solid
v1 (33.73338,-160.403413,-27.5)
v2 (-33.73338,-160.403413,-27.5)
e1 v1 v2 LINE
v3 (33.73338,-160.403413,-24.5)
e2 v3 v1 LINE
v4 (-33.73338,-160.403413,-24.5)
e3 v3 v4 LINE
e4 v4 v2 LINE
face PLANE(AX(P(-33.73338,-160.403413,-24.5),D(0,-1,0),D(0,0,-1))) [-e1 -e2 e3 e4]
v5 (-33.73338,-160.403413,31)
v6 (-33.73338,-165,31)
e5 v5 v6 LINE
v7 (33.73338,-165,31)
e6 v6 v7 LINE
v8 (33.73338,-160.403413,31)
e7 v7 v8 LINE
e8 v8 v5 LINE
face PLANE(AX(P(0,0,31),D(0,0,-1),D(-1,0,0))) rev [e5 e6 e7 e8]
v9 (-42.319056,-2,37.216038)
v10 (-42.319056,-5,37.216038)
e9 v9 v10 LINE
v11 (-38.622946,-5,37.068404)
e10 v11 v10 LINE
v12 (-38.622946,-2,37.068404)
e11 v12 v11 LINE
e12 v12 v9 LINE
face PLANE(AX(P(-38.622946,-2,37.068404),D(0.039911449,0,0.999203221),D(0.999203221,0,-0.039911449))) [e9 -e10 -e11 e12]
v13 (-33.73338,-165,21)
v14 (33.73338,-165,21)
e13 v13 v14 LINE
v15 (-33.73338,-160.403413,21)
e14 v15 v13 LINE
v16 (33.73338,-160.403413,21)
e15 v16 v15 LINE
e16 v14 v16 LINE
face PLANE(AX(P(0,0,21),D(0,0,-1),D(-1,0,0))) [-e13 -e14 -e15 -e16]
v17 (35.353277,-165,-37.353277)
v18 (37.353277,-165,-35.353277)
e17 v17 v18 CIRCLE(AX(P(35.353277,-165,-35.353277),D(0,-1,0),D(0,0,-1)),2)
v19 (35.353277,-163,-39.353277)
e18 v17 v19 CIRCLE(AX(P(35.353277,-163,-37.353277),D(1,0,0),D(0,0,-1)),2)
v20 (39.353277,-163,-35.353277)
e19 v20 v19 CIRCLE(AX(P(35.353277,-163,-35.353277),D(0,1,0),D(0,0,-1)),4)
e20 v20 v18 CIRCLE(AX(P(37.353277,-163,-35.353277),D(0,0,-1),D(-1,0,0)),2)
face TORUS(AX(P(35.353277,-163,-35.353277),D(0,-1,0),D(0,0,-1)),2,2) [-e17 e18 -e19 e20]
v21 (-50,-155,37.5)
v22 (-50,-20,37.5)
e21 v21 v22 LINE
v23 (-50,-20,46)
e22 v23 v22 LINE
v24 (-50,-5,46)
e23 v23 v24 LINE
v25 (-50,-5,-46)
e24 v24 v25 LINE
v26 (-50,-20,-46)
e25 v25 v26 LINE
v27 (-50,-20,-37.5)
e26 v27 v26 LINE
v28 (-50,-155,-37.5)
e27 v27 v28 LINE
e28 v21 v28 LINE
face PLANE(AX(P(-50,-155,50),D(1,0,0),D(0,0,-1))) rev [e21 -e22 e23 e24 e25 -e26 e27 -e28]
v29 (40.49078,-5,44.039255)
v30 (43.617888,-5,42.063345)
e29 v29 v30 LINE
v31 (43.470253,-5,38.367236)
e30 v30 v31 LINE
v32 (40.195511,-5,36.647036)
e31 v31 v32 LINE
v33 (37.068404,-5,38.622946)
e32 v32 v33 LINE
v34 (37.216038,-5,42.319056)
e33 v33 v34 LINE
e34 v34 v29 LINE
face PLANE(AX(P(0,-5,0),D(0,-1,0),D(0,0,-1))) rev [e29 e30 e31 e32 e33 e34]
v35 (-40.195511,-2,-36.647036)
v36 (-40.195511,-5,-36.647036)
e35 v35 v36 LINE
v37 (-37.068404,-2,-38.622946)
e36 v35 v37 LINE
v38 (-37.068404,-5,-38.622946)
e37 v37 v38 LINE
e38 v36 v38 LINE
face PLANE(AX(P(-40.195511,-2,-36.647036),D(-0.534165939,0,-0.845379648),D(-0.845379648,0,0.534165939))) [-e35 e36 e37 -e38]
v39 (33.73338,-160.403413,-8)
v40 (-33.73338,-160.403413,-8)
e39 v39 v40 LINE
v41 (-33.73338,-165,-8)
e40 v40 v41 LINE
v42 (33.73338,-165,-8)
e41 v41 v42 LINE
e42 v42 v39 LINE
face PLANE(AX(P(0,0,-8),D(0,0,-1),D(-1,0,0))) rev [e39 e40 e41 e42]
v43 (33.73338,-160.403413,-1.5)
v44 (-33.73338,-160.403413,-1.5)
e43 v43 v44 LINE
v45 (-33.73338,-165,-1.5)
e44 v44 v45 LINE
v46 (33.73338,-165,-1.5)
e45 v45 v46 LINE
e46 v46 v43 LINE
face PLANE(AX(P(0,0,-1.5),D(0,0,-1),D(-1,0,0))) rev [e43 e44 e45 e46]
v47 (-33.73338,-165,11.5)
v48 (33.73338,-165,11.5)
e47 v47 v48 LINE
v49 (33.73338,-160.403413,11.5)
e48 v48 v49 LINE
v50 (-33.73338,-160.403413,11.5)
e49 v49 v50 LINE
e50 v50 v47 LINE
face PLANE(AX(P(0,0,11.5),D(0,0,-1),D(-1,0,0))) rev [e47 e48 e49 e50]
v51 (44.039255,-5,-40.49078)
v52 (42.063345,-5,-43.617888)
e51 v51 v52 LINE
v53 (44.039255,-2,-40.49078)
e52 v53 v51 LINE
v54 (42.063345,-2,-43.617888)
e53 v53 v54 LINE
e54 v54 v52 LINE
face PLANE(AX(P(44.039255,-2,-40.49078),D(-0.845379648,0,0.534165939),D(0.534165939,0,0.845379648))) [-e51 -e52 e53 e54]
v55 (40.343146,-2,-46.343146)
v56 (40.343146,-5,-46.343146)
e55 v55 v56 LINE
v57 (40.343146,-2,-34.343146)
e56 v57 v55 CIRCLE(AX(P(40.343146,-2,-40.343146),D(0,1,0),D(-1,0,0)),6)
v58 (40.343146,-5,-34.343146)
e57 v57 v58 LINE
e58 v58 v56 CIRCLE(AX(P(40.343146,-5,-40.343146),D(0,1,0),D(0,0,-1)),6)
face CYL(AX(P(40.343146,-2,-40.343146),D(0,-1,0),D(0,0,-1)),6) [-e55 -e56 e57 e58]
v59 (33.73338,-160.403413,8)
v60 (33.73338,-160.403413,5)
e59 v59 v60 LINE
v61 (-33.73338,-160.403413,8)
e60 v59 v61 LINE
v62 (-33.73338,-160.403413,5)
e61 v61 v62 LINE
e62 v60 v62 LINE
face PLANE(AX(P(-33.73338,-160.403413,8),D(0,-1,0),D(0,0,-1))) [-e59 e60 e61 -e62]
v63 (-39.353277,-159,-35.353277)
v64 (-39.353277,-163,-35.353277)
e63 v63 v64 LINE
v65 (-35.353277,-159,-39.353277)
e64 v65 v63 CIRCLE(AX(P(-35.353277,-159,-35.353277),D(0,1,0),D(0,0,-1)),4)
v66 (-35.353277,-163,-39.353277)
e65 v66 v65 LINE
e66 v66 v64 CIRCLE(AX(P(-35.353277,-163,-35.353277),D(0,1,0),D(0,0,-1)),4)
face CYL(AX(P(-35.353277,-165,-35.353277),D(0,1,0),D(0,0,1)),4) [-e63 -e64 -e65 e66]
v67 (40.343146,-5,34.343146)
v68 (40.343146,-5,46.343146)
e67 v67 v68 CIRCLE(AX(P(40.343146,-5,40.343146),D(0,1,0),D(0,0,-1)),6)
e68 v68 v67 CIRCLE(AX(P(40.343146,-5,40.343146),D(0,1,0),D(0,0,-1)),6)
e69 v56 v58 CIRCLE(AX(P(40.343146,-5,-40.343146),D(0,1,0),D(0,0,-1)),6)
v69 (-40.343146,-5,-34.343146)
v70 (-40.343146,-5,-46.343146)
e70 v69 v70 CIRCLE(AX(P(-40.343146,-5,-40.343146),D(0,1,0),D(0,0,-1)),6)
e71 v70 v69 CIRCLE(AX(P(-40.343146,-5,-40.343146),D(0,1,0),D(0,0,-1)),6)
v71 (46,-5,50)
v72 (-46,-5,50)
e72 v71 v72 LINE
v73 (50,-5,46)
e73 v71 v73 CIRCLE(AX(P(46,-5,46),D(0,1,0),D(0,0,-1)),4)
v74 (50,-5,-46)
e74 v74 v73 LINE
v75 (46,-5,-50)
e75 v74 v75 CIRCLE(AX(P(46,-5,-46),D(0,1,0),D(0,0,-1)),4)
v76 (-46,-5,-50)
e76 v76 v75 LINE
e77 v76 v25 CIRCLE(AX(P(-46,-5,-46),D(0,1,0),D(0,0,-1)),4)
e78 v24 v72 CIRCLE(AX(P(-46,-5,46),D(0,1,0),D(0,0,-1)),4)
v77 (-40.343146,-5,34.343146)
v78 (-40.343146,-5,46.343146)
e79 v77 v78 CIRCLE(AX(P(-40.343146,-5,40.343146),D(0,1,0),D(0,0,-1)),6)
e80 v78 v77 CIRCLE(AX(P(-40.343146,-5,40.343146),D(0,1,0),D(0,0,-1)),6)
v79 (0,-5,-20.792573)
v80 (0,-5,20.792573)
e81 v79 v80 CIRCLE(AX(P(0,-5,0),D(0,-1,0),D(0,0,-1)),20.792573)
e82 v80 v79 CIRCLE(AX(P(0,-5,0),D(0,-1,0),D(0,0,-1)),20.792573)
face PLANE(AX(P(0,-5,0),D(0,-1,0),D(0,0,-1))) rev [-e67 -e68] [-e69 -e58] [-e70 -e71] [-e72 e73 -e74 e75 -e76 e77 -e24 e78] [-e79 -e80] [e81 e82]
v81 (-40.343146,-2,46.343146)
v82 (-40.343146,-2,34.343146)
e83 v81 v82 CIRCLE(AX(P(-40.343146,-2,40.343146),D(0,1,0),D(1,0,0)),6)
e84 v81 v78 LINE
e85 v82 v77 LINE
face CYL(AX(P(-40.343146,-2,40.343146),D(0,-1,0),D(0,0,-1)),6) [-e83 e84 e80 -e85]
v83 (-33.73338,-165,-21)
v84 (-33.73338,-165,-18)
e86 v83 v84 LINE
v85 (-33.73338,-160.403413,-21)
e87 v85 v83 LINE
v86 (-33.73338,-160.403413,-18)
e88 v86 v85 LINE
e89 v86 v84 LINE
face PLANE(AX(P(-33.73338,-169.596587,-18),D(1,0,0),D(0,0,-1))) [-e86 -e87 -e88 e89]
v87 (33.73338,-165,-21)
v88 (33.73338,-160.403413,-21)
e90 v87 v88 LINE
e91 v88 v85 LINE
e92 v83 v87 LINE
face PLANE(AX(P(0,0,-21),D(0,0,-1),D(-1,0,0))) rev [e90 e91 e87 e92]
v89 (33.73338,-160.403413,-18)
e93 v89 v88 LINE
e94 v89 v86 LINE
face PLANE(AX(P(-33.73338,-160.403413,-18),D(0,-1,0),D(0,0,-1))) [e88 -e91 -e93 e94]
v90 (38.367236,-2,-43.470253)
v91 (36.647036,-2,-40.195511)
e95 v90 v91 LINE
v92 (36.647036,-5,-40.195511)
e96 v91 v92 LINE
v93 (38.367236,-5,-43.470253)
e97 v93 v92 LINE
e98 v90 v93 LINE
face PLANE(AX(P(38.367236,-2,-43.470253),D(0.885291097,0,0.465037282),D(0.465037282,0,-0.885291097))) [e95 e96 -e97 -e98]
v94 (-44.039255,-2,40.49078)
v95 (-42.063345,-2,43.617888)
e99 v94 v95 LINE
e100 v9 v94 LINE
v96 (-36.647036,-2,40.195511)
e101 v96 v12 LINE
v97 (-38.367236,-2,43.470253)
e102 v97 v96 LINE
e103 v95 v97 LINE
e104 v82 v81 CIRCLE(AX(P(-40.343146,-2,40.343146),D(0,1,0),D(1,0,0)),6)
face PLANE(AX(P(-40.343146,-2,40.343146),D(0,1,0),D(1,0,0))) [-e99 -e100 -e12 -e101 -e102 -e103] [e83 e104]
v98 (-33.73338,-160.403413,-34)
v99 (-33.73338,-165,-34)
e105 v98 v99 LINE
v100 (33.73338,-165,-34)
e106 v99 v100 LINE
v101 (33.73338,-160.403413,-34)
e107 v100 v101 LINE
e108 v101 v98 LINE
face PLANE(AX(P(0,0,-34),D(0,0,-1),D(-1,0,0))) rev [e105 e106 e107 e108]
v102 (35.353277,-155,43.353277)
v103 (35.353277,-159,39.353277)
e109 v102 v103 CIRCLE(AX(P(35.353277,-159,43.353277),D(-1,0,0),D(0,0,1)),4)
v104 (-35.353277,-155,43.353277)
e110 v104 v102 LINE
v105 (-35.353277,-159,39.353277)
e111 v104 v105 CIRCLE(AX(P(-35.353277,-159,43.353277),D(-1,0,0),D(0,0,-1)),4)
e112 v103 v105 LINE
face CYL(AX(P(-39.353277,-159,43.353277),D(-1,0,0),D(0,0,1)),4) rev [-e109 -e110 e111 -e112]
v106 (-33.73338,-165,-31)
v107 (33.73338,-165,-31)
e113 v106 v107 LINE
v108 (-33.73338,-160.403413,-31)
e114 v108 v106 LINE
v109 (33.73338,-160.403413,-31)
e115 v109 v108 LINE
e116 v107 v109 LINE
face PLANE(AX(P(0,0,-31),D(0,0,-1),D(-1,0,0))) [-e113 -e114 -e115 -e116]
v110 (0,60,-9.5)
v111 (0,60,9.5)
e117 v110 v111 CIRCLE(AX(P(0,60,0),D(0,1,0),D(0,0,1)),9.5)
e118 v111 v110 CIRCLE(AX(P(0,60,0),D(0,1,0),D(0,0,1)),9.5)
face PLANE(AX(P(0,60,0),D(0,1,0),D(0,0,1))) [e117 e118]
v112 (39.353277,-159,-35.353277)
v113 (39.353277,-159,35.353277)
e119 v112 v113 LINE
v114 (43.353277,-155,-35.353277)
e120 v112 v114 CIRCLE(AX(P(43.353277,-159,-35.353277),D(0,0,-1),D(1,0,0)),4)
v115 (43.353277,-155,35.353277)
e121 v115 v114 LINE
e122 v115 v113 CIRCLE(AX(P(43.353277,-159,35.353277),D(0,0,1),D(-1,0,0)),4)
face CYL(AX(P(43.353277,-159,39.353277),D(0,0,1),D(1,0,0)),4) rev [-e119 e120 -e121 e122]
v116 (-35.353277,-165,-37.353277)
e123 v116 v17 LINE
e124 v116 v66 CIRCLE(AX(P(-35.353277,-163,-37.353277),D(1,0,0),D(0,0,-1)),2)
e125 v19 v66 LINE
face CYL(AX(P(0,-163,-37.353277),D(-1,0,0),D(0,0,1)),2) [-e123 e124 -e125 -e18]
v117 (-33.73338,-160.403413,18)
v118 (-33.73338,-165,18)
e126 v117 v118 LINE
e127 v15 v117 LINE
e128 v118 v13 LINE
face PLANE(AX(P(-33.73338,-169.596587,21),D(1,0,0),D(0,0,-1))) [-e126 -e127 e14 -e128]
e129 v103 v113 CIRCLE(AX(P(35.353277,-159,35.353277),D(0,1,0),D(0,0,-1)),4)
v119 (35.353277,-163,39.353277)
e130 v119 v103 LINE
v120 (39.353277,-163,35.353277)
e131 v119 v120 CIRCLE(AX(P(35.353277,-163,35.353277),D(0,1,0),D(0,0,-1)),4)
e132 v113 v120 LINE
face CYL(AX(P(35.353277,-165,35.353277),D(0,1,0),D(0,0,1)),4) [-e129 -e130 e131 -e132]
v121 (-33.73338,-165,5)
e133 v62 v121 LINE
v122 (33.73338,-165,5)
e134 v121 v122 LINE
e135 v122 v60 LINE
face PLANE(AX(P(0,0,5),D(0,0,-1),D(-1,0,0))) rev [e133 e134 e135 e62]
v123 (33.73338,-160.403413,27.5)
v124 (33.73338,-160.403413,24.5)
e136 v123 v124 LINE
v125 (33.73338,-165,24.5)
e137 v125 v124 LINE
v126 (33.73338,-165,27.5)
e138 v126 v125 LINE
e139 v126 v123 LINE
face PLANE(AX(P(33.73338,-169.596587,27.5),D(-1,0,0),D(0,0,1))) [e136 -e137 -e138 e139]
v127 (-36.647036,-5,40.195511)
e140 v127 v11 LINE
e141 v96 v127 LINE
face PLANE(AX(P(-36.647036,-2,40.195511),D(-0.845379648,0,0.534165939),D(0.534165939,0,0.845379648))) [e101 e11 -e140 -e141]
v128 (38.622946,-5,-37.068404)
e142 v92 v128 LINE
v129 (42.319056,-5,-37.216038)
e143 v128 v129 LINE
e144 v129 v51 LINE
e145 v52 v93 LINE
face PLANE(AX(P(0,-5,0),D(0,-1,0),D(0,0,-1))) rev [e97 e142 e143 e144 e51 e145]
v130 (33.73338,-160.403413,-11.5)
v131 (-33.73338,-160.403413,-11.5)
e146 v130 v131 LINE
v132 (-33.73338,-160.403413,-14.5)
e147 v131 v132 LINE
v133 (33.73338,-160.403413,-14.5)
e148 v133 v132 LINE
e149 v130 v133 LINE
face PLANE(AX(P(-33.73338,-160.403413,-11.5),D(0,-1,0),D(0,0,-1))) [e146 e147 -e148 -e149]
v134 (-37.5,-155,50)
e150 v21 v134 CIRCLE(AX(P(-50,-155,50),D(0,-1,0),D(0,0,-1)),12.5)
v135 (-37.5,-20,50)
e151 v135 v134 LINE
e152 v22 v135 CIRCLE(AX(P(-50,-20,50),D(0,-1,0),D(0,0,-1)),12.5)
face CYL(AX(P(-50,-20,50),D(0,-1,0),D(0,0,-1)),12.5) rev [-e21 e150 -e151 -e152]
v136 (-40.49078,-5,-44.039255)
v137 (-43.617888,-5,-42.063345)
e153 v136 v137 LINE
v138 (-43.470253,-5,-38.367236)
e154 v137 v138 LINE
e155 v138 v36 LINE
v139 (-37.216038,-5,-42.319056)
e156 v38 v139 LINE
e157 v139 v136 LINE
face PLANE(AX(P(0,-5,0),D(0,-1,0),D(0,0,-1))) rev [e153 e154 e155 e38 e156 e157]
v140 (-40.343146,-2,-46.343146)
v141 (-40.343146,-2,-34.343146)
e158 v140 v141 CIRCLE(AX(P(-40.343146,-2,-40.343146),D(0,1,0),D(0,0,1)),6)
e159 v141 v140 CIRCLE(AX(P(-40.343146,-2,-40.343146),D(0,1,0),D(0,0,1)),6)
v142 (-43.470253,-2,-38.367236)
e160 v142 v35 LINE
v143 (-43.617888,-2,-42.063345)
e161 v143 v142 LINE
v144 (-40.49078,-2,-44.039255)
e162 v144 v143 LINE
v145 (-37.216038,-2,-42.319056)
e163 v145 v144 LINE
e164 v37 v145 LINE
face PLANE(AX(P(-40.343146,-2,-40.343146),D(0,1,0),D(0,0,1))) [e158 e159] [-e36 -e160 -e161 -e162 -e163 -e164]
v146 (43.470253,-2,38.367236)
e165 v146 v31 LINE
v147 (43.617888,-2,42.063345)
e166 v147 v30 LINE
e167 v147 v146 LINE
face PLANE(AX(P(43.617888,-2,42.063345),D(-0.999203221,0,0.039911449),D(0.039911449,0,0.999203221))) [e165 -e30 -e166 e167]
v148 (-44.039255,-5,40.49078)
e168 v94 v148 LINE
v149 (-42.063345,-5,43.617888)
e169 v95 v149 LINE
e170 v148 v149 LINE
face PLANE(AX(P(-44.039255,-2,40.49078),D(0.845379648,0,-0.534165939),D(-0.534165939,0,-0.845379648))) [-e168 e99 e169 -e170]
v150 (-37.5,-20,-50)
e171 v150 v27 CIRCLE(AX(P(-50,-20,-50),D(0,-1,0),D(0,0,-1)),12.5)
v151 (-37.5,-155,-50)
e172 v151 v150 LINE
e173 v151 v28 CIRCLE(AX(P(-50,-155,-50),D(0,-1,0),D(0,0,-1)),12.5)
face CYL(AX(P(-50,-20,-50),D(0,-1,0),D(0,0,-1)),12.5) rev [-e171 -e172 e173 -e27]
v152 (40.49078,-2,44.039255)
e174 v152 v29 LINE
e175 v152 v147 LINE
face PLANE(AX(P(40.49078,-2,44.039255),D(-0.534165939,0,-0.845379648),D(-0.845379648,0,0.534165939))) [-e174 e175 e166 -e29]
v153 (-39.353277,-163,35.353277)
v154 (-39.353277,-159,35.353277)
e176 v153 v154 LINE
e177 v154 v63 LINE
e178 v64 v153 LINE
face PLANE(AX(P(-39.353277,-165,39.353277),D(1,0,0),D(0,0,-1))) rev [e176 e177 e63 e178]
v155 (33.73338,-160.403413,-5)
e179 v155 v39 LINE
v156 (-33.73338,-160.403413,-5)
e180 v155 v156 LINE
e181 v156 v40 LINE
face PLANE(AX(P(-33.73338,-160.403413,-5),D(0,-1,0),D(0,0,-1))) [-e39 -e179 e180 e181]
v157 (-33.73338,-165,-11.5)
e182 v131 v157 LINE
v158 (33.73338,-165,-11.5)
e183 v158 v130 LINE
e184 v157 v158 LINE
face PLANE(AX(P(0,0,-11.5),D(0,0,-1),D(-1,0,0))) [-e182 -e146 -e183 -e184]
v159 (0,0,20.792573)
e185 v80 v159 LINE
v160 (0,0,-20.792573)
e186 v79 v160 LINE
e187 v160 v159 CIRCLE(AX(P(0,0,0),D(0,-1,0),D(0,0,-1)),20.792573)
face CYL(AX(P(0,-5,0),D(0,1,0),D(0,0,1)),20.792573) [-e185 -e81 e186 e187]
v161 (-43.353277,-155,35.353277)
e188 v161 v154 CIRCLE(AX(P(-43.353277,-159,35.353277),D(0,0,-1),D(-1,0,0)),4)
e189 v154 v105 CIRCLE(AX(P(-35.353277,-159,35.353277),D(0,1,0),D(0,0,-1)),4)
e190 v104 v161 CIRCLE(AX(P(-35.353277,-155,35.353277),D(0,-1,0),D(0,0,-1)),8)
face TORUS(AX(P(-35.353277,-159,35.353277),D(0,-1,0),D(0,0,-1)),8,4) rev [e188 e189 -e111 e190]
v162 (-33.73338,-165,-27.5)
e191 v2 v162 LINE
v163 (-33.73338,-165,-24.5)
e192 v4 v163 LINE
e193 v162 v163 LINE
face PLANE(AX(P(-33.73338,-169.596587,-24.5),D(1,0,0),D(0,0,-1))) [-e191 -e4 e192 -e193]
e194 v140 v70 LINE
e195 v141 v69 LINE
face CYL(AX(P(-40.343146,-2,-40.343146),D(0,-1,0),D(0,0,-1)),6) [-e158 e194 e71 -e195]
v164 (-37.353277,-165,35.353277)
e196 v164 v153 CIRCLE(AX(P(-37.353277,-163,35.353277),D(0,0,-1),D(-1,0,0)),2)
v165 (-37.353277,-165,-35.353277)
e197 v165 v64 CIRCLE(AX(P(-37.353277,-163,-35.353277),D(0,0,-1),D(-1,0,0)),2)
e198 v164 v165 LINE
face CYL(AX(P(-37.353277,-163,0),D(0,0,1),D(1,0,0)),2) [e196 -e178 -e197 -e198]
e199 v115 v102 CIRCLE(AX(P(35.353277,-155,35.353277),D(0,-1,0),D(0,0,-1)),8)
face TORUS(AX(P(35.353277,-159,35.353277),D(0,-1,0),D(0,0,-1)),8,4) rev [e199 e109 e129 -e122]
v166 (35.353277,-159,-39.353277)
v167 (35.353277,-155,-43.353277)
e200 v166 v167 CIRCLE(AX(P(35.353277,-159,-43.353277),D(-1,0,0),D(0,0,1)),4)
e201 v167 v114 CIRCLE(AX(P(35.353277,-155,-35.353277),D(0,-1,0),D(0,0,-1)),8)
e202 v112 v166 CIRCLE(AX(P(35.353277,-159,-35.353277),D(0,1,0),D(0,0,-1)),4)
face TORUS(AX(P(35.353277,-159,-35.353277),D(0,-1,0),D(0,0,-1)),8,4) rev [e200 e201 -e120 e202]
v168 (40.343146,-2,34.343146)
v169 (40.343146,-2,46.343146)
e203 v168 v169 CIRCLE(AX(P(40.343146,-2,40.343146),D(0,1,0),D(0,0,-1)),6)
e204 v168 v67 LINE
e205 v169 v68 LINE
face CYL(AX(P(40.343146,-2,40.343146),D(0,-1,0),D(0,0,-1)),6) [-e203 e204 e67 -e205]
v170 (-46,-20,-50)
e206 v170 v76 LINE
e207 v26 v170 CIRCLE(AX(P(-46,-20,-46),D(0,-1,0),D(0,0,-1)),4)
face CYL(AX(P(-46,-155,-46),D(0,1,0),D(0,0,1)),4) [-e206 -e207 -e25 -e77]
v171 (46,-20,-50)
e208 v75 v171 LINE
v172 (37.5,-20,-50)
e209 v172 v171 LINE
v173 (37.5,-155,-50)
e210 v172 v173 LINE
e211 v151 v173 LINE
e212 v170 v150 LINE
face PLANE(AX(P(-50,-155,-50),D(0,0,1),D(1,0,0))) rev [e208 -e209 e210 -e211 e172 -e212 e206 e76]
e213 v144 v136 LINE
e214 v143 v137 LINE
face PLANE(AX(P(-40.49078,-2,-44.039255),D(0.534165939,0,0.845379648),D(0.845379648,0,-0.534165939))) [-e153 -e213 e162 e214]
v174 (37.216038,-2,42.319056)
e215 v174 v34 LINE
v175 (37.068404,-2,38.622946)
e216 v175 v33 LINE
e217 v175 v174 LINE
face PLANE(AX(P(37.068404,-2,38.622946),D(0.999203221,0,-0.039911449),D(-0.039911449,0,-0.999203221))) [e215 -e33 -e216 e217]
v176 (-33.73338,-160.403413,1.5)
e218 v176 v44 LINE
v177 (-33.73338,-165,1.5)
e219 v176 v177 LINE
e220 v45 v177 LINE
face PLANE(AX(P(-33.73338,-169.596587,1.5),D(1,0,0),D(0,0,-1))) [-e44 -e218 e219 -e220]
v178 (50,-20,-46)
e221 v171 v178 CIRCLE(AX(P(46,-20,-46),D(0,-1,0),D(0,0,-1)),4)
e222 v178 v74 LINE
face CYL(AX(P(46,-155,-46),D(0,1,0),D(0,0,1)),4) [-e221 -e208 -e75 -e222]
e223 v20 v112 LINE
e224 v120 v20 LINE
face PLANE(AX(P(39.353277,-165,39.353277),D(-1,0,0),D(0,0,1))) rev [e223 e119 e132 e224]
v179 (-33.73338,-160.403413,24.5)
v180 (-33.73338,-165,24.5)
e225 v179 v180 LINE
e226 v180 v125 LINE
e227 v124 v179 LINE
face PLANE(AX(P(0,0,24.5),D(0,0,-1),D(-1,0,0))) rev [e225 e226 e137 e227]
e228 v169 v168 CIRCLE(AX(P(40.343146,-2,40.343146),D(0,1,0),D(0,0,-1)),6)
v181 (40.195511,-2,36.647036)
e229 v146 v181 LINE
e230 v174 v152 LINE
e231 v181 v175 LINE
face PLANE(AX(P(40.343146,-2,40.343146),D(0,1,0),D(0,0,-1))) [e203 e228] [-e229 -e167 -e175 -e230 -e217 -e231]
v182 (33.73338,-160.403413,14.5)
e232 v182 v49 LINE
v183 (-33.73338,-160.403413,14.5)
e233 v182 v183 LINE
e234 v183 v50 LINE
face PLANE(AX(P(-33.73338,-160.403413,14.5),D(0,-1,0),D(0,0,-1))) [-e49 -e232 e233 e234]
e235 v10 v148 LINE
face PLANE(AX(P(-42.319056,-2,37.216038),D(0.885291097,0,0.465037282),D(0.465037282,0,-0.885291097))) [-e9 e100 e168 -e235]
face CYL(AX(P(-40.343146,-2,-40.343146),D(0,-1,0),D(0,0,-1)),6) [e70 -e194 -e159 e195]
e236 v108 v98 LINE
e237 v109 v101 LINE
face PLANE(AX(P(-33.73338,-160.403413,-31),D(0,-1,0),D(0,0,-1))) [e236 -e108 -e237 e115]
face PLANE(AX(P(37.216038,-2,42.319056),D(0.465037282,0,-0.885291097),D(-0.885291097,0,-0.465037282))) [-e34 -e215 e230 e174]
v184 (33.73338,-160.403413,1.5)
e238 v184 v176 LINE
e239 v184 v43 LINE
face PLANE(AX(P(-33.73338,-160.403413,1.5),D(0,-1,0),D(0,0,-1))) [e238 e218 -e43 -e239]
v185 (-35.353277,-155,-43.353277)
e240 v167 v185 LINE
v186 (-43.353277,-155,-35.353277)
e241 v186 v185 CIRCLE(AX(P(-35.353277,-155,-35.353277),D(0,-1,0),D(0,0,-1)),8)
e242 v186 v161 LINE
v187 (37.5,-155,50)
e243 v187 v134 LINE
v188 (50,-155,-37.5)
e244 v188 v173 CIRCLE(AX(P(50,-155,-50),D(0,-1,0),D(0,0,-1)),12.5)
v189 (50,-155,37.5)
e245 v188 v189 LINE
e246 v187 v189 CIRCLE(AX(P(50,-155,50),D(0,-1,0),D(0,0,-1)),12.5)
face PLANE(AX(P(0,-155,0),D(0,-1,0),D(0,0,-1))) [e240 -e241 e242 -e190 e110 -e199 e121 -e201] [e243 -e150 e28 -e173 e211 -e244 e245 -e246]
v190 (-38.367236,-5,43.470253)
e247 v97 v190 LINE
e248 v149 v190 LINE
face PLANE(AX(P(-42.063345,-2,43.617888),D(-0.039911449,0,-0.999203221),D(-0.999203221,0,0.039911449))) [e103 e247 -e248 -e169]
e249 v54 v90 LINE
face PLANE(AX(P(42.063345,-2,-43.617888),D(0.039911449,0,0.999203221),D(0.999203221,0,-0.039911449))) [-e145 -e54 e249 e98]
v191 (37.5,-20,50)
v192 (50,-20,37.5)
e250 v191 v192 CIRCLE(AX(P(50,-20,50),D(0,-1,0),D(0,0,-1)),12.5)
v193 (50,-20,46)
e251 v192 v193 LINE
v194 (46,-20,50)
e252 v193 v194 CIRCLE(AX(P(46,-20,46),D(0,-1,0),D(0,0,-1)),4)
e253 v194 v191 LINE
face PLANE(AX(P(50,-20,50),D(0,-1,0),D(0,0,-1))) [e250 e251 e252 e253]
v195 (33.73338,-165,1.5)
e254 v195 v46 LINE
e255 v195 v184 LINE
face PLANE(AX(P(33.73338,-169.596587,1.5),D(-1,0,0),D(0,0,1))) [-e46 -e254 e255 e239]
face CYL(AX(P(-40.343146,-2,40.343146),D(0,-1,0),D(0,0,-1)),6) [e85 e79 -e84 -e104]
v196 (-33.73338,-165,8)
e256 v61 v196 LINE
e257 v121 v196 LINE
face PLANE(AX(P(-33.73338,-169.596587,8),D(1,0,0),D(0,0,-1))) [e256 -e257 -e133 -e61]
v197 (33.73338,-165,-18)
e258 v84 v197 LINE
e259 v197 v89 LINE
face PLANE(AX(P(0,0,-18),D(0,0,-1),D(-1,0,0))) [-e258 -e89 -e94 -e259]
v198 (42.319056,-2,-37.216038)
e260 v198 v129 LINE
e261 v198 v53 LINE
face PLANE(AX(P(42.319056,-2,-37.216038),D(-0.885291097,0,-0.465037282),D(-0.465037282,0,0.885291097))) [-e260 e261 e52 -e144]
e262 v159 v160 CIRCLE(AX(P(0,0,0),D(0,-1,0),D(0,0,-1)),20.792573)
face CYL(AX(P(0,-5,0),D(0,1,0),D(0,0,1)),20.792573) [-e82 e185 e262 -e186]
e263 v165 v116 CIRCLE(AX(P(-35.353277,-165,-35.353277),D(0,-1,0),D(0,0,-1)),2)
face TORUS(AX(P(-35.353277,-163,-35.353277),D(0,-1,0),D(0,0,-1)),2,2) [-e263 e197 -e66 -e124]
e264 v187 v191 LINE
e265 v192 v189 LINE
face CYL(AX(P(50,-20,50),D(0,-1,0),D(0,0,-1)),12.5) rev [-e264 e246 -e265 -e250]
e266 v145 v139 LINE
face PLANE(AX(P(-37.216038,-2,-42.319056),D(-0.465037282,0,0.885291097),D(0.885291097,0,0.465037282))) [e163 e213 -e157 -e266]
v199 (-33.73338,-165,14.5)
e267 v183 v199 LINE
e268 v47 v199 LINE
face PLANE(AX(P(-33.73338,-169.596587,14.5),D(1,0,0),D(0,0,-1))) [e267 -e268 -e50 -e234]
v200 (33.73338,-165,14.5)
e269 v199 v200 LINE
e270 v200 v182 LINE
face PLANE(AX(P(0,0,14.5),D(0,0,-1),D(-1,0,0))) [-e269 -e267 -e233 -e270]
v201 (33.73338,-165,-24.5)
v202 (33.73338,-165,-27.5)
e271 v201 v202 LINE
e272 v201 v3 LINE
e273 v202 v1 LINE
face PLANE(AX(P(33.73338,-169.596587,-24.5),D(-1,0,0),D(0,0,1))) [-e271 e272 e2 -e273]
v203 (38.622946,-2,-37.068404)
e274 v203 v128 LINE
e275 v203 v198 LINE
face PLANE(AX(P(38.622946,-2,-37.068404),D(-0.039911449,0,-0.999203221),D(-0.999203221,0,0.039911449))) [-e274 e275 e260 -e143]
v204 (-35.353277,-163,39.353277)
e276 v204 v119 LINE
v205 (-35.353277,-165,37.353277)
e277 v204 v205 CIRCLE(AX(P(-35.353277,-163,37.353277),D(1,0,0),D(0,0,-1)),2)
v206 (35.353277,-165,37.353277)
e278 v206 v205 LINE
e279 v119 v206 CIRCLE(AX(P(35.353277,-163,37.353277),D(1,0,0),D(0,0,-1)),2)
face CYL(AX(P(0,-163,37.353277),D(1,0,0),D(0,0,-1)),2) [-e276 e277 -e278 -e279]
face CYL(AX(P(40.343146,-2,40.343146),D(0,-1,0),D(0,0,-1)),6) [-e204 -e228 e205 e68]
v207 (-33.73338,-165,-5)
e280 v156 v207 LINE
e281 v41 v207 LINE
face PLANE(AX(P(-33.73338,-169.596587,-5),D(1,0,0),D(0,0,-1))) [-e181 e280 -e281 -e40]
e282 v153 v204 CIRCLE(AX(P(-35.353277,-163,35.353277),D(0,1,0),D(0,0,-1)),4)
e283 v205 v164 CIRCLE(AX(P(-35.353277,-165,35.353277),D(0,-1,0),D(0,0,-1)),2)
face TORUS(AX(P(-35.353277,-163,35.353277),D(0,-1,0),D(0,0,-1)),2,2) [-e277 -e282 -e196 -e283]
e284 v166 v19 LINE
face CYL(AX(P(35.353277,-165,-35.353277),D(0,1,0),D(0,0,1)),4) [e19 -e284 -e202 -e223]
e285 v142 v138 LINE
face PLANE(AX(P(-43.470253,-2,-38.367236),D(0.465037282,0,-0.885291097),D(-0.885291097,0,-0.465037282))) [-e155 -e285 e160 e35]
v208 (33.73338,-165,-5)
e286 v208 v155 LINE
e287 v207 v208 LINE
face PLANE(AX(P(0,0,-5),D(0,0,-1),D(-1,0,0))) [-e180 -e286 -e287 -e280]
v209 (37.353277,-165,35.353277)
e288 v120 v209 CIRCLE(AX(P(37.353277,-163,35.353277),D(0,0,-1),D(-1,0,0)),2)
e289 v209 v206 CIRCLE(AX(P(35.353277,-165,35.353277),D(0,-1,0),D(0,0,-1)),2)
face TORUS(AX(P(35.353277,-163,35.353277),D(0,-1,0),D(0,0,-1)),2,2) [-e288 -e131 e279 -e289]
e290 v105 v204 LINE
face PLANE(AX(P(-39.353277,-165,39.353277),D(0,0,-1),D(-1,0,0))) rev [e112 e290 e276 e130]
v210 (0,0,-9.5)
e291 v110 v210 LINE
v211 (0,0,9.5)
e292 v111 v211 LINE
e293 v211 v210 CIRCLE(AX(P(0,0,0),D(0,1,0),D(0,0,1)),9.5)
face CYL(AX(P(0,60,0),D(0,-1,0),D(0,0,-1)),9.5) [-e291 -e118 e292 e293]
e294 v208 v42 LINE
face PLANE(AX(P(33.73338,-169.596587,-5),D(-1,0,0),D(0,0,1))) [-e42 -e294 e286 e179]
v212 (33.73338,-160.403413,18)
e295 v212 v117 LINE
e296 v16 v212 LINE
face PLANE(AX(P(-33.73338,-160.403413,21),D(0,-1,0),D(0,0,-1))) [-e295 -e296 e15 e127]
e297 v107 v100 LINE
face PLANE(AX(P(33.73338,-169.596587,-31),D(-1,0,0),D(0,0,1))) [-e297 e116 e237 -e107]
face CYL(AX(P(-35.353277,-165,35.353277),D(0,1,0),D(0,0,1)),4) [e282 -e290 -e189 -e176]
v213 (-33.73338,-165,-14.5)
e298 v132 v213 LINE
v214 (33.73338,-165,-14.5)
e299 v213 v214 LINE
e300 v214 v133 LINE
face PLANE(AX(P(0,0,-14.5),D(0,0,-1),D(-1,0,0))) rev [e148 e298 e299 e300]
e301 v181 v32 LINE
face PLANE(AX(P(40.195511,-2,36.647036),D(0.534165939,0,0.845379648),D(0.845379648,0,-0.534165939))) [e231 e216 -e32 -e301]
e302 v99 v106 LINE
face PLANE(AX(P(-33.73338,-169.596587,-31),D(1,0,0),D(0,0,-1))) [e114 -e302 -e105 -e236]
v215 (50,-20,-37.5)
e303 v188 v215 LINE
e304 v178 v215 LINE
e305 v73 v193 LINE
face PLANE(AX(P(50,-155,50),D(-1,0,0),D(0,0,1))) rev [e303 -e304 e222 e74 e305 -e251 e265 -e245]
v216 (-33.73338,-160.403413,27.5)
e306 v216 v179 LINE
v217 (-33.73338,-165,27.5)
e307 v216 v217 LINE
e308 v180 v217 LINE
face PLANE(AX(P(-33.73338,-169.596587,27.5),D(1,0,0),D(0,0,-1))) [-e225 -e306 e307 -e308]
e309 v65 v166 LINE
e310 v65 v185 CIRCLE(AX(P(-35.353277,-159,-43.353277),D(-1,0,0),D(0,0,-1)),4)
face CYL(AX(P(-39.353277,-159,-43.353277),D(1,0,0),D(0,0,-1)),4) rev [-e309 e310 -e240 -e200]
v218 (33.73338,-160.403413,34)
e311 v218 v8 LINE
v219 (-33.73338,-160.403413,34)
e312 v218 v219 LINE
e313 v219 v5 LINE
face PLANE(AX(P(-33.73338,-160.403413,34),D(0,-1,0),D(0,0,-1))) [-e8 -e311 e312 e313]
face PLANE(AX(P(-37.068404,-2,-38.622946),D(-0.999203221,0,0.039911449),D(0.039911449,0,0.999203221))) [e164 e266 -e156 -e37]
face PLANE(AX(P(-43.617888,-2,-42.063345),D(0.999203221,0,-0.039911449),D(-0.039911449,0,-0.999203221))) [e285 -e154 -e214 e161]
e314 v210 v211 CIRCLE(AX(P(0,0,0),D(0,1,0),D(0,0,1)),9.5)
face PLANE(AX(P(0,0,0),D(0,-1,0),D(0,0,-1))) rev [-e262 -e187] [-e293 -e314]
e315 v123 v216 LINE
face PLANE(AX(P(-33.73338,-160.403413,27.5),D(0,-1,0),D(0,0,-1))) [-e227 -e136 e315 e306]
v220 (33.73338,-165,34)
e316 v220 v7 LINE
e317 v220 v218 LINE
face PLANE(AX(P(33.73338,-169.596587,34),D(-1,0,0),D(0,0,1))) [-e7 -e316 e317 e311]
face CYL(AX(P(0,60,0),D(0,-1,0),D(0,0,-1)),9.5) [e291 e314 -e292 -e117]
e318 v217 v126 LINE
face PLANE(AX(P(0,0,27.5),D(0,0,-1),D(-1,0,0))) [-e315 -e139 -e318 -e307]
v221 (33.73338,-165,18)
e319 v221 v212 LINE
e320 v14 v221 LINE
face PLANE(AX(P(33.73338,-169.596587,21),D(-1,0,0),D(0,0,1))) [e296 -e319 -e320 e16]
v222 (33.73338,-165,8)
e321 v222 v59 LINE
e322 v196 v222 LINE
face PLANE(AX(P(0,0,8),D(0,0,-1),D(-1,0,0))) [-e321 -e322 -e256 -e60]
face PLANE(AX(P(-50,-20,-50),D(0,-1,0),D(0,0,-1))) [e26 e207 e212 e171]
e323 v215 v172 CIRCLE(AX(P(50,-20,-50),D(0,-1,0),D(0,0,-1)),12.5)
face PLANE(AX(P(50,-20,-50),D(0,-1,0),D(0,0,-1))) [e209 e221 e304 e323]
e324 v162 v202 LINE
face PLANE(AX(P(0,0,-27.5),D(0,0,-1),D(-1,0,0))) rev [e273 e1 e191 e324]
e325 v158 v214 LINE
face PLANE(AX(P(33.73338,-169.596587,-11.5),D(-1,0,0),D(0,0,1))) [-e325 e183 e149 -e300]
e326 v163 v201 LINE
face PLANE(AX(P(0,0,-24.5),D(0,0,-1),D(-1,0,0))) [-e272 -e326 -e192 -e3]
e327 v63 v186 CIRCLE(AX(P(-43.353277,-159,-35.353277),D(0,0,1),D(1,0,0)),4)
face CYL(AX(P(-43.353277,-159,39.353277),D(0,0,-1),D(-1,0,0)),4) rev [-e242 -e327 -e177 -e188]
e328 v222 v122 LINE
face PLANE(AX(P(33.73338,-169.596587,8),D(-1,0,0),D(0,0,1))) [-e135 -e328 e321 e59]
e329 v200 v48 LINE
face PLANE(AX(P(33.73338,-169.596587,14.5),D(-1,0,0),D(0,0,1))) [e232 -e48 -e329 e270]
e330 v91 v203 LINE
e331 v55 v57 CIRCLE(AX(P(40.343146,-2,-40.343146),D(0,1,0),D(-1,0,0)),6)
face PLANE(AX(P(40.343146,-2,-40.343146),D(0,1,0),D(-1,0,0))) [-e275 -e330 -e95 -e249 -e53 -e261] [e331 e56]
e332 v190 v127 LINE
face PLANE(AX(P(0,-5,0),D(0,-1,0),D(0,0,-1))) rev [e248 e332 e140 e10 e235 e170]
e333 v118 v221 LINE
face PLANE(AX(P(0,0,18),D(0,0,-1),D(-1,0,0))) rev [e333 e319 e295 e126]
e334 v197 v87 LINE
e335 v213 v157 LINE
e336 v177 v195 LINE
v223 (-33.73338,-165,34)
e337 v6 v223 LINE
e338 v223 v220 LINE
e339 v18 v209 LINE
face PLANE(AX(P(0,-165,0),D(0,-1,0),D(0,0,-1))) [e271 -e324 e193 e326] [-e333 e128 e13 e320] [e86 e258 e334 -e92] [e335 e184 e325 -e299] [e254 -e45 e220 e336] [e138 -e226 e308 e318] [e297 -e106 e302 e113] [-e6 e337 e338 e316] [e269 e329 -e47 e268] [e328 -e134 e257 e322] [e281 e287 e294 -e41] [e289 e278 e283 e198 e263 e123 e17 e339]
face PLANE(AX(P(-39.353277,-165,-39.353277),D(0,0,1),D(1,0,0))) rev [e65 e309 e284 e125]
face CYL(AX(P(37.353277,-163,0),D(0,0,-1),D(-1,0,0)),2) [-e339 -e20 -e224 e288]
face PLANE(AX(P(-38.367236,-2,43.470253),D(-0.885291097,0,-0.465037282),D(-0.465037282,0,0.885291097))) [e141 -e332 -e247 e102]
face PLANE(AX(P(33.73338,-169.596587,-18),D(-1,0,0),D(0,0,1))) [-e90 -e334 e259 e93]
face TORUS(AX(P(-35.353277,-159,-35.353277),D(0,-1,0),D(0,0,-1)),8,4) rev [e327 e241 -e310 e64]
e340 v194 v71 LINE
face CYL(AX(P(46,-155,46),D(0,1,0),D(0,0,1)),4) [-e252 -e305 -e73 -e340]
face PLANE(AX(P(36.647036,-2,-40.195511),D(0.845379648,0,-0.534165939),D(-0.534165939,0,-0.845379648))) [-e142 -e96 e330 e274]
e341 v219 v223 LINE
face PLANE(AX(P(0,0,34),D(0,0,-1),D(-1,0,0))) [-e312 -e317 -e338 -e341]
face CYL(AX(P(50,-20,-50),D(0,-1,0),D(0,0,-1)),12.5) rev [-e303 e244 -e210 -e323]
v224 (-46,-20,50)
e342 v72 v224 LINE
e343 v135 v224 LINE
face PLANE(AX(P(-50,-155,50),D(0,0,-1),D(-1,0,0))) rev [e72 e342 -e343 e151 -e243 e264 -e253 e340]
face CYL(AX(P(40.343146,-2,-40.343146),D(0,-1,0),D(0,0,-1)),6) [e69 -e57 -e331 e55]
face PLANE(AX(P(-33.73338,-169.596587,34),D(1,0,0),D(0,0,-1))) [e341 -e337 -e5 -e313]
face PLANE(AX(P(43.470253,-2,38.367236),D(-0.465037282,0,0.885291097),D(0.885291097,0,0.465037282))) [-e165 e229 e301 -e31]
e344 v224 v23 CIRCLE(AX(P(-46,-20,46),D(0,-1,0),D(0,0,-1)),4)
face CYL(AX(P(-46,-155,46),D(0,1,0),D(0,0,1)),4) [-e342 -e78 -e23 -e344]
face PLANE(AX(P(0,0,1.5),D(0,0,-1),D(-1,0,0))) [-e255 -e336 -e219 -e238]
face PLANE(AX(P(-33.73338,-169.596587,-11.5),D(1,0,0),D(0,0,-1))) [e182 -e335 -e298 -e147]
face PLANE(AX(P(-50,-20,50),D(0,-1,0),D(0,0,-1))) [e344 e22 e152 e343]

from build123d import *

# Parameters (mm, degrees)
SKETCH1_R           = 9.5
BOSS_EXTRUDE1_DEPTH = 60
SKETCH2_R           = 20.792572887
BOSS_EXTRUDE2_DEPTH = 5
SKETCH3_W           = 100
SKETCH3_H           = 100
BOSS_EXTRUDE3_DEPTH = 150
SKETCH4_R           = 12.5
CUT_EXTRUDE1_DEPTH  = 135
FILLET1_R           = 4
SKETCH5_W           = 78.706554356
SKETCH5_H           = 78.706554356
BOSS_EXTRUDE4_DEPTH = 10
FILLET2_R           = 4
FILLET3_R           = 2
SKETCH6_W           = 67.46675987
SKETCH6_H           = 9.193174248
CUT_EXTRUDE2_DEPTH  = 1.5
LPATTERN1_COUNT     = 6
LPATTERN1_PITCH     = 6.5
LPATTERN1_COL_COUNT = 6
LPATTERN1_COL_PITCH = 6.5
SKETCH7_R           = 6
BOSS_EXTRUDE5_DEPTH = 3
CIRPATTERN1_COUNT   = 4


with BuildPart() as part:
    # Sketch1 → Boss-Extrude1 (new body)
    with BuildSketch(Plane(origin=(0, 0, 0), x_dir=(1, 0, 0), z_dir=(0, 1, 0))):
        with Locations(Location((0, 0, 0), (0, 0, 270))):
            Circle(SKETCH1_R)
    extrude(amount=BOSS_EXTRUDE1_DEPTH)

    # Sketch2 → Boss-Extrude2 (add)
    with BuildSketch(Plane.XZ):
        with Locations(Location((0, 0, 0), (0, 0, 270))):
            Circle(SKETCH2_R)
    extrude(amount=BOSS_EXTRUDE2_DEPTH)

    # Sketch3 → Boss-Extrude3 (add)
    with BuildSketch(Plane.XZ.offset(5)):
        Rectangle(SKETCH3_W, SKETCH3_H)
    extrude(amount=BOSS_EXTRUDE3_DEPTH)

    # Sketch4 → Cut-Extrude1 (cut)
    with BuildSketch(Plane.XZ.offset(155)):
        with Locations((-50, 50)):
            Circle(SKETCH4_R)
        with Locations((50, 50)):
            Circle(SKETCH4_R)
        with Locations((-50, -50)):
            Circle(SKETCH4_R)
        with Locations((50, -50)):
            Circle(SKETCH4_R)
    extrude(amount=-CUT_EXTRUDE1_DEPTH, mode=Mode.SUBTRACT)

    # Fillet1
    fillet1_edges = [part.edges().sort_by_distance(p)[0] for p in [
        (50, -12.5, -50),
        (-50, -12.5, -50),
        (-50, -12.5, 50),
        (50, -12.5, 50),
    ]]
    fillet(fillet1_edges, radius=FILLET1_R)

    # Sketch5 → Boss-Extrude4 (add)
    with BuildSketch(Plane.XZ.offset(155)):
        Rectangle(SKETCH5_W, SKETCH5_H)
    extrude(amount=BOSS_EXTRUDE4_DEPTH)

    # Fillet2
    fillet2_edges = [part.edges().sort_by_distance(p)[0] for p in [
        (39.353277178, -155, 0),
        (39.353277178, -160, -39.353277178),
        (0, -155, 39.353277178),
        (39.353277178, -160, 39.353277178),
        (-39.353277178, -155, 0),
        (-39.353277178, -160, 39.353277178),
        (0, -155, -39.353277178),
        (-39.353277178, -160, -39.353277178),
    ]]
    fillet(fillet2_edges, radius=FILLET2_R)

    # Fillet3
    fillet3_edges = [part.edges().sort_by_distance(p)[0] for p in [
        (39.353277178, -165, 0),
        (0, -165, 39.353277178),
        (-39.353277178, -165, 0),
        (0, -165, -39.353277178),
        (38.181704302, -165, -38.181704302),
        (-38.181704302, -165, -38.181704302),
        (-38.181704302, -165, 38.181704302),
        (38.181704302, -165, 38.181704302),
    ]]
    fillet(fillet3_edges, radius=FILLET3_R)

    # Sketch6 → Cut-Extrude2 (cut, symmetric)
    with BuildSketch(Plane.XY):
        with Locations((0, -165)):
            Rectangle(SKETCH6_W, SKETCH6_H)
    cut_extrude2 = extrude(amount=CUT_EXTRUDE2_DEPTH, both=True, mode=Mode.SUBTRACT)

    # LPattern1: Cut-Extrude2 ×6
    with Locations(*[(0, 0, i * LPATTERN1_PITCH) for i in range(1, LPATTERN1_COUNT)]):
        add(cut_extrude2, mode=Mode.SUBTRACT)

    # LPattern1 col: Cut-Extrude2 ×6
    with Locations(*[(0, 0, -i * LPATTERN1_COL_PITCH) for i in range(1, LPATTERN1_COL_COUNT)]):
        add(cut_extrude2, mode=Mode.SUBTRACT)

    # Sketch7 → Boss-Extrude5 (add)
    with BuildSketch(Plane(origin=(0, -5, 0), x_dir=(1, 0, 0), z_dir=(0, 1, 0))):
        with Locations(Location((-40.343145751, 40.343145751, 0), (0, 0, 90))):
            Circle(SKETCH7_R)
        Polygon((-37.068403744, 38.622946456), (-37.216038458, 42.319055872), (-40.490780465, 44.039255167), (-43.617887757, 42.063345045), (-43.470253043, 38.367235629), (-40.195511036, 36.647036334), align=None, mode=Mode.SUBTRACT)
    boss_extrude5 = extrude(amount=BOSS_EXTRUDE5_DEPTH)

    # CirPattern1: Boss-Extrude5 ×4 about axis
    cirpattern1_axis = Axis((0, 0, 0), (0, 1, 0))
    for i in range(1, CIRPATTERN1_COUNT):
        add(boss_extrude5.rotate(cirpattern1_axis, i * 360 / CIRPATTERN1_COUNT))


solid = part.part
